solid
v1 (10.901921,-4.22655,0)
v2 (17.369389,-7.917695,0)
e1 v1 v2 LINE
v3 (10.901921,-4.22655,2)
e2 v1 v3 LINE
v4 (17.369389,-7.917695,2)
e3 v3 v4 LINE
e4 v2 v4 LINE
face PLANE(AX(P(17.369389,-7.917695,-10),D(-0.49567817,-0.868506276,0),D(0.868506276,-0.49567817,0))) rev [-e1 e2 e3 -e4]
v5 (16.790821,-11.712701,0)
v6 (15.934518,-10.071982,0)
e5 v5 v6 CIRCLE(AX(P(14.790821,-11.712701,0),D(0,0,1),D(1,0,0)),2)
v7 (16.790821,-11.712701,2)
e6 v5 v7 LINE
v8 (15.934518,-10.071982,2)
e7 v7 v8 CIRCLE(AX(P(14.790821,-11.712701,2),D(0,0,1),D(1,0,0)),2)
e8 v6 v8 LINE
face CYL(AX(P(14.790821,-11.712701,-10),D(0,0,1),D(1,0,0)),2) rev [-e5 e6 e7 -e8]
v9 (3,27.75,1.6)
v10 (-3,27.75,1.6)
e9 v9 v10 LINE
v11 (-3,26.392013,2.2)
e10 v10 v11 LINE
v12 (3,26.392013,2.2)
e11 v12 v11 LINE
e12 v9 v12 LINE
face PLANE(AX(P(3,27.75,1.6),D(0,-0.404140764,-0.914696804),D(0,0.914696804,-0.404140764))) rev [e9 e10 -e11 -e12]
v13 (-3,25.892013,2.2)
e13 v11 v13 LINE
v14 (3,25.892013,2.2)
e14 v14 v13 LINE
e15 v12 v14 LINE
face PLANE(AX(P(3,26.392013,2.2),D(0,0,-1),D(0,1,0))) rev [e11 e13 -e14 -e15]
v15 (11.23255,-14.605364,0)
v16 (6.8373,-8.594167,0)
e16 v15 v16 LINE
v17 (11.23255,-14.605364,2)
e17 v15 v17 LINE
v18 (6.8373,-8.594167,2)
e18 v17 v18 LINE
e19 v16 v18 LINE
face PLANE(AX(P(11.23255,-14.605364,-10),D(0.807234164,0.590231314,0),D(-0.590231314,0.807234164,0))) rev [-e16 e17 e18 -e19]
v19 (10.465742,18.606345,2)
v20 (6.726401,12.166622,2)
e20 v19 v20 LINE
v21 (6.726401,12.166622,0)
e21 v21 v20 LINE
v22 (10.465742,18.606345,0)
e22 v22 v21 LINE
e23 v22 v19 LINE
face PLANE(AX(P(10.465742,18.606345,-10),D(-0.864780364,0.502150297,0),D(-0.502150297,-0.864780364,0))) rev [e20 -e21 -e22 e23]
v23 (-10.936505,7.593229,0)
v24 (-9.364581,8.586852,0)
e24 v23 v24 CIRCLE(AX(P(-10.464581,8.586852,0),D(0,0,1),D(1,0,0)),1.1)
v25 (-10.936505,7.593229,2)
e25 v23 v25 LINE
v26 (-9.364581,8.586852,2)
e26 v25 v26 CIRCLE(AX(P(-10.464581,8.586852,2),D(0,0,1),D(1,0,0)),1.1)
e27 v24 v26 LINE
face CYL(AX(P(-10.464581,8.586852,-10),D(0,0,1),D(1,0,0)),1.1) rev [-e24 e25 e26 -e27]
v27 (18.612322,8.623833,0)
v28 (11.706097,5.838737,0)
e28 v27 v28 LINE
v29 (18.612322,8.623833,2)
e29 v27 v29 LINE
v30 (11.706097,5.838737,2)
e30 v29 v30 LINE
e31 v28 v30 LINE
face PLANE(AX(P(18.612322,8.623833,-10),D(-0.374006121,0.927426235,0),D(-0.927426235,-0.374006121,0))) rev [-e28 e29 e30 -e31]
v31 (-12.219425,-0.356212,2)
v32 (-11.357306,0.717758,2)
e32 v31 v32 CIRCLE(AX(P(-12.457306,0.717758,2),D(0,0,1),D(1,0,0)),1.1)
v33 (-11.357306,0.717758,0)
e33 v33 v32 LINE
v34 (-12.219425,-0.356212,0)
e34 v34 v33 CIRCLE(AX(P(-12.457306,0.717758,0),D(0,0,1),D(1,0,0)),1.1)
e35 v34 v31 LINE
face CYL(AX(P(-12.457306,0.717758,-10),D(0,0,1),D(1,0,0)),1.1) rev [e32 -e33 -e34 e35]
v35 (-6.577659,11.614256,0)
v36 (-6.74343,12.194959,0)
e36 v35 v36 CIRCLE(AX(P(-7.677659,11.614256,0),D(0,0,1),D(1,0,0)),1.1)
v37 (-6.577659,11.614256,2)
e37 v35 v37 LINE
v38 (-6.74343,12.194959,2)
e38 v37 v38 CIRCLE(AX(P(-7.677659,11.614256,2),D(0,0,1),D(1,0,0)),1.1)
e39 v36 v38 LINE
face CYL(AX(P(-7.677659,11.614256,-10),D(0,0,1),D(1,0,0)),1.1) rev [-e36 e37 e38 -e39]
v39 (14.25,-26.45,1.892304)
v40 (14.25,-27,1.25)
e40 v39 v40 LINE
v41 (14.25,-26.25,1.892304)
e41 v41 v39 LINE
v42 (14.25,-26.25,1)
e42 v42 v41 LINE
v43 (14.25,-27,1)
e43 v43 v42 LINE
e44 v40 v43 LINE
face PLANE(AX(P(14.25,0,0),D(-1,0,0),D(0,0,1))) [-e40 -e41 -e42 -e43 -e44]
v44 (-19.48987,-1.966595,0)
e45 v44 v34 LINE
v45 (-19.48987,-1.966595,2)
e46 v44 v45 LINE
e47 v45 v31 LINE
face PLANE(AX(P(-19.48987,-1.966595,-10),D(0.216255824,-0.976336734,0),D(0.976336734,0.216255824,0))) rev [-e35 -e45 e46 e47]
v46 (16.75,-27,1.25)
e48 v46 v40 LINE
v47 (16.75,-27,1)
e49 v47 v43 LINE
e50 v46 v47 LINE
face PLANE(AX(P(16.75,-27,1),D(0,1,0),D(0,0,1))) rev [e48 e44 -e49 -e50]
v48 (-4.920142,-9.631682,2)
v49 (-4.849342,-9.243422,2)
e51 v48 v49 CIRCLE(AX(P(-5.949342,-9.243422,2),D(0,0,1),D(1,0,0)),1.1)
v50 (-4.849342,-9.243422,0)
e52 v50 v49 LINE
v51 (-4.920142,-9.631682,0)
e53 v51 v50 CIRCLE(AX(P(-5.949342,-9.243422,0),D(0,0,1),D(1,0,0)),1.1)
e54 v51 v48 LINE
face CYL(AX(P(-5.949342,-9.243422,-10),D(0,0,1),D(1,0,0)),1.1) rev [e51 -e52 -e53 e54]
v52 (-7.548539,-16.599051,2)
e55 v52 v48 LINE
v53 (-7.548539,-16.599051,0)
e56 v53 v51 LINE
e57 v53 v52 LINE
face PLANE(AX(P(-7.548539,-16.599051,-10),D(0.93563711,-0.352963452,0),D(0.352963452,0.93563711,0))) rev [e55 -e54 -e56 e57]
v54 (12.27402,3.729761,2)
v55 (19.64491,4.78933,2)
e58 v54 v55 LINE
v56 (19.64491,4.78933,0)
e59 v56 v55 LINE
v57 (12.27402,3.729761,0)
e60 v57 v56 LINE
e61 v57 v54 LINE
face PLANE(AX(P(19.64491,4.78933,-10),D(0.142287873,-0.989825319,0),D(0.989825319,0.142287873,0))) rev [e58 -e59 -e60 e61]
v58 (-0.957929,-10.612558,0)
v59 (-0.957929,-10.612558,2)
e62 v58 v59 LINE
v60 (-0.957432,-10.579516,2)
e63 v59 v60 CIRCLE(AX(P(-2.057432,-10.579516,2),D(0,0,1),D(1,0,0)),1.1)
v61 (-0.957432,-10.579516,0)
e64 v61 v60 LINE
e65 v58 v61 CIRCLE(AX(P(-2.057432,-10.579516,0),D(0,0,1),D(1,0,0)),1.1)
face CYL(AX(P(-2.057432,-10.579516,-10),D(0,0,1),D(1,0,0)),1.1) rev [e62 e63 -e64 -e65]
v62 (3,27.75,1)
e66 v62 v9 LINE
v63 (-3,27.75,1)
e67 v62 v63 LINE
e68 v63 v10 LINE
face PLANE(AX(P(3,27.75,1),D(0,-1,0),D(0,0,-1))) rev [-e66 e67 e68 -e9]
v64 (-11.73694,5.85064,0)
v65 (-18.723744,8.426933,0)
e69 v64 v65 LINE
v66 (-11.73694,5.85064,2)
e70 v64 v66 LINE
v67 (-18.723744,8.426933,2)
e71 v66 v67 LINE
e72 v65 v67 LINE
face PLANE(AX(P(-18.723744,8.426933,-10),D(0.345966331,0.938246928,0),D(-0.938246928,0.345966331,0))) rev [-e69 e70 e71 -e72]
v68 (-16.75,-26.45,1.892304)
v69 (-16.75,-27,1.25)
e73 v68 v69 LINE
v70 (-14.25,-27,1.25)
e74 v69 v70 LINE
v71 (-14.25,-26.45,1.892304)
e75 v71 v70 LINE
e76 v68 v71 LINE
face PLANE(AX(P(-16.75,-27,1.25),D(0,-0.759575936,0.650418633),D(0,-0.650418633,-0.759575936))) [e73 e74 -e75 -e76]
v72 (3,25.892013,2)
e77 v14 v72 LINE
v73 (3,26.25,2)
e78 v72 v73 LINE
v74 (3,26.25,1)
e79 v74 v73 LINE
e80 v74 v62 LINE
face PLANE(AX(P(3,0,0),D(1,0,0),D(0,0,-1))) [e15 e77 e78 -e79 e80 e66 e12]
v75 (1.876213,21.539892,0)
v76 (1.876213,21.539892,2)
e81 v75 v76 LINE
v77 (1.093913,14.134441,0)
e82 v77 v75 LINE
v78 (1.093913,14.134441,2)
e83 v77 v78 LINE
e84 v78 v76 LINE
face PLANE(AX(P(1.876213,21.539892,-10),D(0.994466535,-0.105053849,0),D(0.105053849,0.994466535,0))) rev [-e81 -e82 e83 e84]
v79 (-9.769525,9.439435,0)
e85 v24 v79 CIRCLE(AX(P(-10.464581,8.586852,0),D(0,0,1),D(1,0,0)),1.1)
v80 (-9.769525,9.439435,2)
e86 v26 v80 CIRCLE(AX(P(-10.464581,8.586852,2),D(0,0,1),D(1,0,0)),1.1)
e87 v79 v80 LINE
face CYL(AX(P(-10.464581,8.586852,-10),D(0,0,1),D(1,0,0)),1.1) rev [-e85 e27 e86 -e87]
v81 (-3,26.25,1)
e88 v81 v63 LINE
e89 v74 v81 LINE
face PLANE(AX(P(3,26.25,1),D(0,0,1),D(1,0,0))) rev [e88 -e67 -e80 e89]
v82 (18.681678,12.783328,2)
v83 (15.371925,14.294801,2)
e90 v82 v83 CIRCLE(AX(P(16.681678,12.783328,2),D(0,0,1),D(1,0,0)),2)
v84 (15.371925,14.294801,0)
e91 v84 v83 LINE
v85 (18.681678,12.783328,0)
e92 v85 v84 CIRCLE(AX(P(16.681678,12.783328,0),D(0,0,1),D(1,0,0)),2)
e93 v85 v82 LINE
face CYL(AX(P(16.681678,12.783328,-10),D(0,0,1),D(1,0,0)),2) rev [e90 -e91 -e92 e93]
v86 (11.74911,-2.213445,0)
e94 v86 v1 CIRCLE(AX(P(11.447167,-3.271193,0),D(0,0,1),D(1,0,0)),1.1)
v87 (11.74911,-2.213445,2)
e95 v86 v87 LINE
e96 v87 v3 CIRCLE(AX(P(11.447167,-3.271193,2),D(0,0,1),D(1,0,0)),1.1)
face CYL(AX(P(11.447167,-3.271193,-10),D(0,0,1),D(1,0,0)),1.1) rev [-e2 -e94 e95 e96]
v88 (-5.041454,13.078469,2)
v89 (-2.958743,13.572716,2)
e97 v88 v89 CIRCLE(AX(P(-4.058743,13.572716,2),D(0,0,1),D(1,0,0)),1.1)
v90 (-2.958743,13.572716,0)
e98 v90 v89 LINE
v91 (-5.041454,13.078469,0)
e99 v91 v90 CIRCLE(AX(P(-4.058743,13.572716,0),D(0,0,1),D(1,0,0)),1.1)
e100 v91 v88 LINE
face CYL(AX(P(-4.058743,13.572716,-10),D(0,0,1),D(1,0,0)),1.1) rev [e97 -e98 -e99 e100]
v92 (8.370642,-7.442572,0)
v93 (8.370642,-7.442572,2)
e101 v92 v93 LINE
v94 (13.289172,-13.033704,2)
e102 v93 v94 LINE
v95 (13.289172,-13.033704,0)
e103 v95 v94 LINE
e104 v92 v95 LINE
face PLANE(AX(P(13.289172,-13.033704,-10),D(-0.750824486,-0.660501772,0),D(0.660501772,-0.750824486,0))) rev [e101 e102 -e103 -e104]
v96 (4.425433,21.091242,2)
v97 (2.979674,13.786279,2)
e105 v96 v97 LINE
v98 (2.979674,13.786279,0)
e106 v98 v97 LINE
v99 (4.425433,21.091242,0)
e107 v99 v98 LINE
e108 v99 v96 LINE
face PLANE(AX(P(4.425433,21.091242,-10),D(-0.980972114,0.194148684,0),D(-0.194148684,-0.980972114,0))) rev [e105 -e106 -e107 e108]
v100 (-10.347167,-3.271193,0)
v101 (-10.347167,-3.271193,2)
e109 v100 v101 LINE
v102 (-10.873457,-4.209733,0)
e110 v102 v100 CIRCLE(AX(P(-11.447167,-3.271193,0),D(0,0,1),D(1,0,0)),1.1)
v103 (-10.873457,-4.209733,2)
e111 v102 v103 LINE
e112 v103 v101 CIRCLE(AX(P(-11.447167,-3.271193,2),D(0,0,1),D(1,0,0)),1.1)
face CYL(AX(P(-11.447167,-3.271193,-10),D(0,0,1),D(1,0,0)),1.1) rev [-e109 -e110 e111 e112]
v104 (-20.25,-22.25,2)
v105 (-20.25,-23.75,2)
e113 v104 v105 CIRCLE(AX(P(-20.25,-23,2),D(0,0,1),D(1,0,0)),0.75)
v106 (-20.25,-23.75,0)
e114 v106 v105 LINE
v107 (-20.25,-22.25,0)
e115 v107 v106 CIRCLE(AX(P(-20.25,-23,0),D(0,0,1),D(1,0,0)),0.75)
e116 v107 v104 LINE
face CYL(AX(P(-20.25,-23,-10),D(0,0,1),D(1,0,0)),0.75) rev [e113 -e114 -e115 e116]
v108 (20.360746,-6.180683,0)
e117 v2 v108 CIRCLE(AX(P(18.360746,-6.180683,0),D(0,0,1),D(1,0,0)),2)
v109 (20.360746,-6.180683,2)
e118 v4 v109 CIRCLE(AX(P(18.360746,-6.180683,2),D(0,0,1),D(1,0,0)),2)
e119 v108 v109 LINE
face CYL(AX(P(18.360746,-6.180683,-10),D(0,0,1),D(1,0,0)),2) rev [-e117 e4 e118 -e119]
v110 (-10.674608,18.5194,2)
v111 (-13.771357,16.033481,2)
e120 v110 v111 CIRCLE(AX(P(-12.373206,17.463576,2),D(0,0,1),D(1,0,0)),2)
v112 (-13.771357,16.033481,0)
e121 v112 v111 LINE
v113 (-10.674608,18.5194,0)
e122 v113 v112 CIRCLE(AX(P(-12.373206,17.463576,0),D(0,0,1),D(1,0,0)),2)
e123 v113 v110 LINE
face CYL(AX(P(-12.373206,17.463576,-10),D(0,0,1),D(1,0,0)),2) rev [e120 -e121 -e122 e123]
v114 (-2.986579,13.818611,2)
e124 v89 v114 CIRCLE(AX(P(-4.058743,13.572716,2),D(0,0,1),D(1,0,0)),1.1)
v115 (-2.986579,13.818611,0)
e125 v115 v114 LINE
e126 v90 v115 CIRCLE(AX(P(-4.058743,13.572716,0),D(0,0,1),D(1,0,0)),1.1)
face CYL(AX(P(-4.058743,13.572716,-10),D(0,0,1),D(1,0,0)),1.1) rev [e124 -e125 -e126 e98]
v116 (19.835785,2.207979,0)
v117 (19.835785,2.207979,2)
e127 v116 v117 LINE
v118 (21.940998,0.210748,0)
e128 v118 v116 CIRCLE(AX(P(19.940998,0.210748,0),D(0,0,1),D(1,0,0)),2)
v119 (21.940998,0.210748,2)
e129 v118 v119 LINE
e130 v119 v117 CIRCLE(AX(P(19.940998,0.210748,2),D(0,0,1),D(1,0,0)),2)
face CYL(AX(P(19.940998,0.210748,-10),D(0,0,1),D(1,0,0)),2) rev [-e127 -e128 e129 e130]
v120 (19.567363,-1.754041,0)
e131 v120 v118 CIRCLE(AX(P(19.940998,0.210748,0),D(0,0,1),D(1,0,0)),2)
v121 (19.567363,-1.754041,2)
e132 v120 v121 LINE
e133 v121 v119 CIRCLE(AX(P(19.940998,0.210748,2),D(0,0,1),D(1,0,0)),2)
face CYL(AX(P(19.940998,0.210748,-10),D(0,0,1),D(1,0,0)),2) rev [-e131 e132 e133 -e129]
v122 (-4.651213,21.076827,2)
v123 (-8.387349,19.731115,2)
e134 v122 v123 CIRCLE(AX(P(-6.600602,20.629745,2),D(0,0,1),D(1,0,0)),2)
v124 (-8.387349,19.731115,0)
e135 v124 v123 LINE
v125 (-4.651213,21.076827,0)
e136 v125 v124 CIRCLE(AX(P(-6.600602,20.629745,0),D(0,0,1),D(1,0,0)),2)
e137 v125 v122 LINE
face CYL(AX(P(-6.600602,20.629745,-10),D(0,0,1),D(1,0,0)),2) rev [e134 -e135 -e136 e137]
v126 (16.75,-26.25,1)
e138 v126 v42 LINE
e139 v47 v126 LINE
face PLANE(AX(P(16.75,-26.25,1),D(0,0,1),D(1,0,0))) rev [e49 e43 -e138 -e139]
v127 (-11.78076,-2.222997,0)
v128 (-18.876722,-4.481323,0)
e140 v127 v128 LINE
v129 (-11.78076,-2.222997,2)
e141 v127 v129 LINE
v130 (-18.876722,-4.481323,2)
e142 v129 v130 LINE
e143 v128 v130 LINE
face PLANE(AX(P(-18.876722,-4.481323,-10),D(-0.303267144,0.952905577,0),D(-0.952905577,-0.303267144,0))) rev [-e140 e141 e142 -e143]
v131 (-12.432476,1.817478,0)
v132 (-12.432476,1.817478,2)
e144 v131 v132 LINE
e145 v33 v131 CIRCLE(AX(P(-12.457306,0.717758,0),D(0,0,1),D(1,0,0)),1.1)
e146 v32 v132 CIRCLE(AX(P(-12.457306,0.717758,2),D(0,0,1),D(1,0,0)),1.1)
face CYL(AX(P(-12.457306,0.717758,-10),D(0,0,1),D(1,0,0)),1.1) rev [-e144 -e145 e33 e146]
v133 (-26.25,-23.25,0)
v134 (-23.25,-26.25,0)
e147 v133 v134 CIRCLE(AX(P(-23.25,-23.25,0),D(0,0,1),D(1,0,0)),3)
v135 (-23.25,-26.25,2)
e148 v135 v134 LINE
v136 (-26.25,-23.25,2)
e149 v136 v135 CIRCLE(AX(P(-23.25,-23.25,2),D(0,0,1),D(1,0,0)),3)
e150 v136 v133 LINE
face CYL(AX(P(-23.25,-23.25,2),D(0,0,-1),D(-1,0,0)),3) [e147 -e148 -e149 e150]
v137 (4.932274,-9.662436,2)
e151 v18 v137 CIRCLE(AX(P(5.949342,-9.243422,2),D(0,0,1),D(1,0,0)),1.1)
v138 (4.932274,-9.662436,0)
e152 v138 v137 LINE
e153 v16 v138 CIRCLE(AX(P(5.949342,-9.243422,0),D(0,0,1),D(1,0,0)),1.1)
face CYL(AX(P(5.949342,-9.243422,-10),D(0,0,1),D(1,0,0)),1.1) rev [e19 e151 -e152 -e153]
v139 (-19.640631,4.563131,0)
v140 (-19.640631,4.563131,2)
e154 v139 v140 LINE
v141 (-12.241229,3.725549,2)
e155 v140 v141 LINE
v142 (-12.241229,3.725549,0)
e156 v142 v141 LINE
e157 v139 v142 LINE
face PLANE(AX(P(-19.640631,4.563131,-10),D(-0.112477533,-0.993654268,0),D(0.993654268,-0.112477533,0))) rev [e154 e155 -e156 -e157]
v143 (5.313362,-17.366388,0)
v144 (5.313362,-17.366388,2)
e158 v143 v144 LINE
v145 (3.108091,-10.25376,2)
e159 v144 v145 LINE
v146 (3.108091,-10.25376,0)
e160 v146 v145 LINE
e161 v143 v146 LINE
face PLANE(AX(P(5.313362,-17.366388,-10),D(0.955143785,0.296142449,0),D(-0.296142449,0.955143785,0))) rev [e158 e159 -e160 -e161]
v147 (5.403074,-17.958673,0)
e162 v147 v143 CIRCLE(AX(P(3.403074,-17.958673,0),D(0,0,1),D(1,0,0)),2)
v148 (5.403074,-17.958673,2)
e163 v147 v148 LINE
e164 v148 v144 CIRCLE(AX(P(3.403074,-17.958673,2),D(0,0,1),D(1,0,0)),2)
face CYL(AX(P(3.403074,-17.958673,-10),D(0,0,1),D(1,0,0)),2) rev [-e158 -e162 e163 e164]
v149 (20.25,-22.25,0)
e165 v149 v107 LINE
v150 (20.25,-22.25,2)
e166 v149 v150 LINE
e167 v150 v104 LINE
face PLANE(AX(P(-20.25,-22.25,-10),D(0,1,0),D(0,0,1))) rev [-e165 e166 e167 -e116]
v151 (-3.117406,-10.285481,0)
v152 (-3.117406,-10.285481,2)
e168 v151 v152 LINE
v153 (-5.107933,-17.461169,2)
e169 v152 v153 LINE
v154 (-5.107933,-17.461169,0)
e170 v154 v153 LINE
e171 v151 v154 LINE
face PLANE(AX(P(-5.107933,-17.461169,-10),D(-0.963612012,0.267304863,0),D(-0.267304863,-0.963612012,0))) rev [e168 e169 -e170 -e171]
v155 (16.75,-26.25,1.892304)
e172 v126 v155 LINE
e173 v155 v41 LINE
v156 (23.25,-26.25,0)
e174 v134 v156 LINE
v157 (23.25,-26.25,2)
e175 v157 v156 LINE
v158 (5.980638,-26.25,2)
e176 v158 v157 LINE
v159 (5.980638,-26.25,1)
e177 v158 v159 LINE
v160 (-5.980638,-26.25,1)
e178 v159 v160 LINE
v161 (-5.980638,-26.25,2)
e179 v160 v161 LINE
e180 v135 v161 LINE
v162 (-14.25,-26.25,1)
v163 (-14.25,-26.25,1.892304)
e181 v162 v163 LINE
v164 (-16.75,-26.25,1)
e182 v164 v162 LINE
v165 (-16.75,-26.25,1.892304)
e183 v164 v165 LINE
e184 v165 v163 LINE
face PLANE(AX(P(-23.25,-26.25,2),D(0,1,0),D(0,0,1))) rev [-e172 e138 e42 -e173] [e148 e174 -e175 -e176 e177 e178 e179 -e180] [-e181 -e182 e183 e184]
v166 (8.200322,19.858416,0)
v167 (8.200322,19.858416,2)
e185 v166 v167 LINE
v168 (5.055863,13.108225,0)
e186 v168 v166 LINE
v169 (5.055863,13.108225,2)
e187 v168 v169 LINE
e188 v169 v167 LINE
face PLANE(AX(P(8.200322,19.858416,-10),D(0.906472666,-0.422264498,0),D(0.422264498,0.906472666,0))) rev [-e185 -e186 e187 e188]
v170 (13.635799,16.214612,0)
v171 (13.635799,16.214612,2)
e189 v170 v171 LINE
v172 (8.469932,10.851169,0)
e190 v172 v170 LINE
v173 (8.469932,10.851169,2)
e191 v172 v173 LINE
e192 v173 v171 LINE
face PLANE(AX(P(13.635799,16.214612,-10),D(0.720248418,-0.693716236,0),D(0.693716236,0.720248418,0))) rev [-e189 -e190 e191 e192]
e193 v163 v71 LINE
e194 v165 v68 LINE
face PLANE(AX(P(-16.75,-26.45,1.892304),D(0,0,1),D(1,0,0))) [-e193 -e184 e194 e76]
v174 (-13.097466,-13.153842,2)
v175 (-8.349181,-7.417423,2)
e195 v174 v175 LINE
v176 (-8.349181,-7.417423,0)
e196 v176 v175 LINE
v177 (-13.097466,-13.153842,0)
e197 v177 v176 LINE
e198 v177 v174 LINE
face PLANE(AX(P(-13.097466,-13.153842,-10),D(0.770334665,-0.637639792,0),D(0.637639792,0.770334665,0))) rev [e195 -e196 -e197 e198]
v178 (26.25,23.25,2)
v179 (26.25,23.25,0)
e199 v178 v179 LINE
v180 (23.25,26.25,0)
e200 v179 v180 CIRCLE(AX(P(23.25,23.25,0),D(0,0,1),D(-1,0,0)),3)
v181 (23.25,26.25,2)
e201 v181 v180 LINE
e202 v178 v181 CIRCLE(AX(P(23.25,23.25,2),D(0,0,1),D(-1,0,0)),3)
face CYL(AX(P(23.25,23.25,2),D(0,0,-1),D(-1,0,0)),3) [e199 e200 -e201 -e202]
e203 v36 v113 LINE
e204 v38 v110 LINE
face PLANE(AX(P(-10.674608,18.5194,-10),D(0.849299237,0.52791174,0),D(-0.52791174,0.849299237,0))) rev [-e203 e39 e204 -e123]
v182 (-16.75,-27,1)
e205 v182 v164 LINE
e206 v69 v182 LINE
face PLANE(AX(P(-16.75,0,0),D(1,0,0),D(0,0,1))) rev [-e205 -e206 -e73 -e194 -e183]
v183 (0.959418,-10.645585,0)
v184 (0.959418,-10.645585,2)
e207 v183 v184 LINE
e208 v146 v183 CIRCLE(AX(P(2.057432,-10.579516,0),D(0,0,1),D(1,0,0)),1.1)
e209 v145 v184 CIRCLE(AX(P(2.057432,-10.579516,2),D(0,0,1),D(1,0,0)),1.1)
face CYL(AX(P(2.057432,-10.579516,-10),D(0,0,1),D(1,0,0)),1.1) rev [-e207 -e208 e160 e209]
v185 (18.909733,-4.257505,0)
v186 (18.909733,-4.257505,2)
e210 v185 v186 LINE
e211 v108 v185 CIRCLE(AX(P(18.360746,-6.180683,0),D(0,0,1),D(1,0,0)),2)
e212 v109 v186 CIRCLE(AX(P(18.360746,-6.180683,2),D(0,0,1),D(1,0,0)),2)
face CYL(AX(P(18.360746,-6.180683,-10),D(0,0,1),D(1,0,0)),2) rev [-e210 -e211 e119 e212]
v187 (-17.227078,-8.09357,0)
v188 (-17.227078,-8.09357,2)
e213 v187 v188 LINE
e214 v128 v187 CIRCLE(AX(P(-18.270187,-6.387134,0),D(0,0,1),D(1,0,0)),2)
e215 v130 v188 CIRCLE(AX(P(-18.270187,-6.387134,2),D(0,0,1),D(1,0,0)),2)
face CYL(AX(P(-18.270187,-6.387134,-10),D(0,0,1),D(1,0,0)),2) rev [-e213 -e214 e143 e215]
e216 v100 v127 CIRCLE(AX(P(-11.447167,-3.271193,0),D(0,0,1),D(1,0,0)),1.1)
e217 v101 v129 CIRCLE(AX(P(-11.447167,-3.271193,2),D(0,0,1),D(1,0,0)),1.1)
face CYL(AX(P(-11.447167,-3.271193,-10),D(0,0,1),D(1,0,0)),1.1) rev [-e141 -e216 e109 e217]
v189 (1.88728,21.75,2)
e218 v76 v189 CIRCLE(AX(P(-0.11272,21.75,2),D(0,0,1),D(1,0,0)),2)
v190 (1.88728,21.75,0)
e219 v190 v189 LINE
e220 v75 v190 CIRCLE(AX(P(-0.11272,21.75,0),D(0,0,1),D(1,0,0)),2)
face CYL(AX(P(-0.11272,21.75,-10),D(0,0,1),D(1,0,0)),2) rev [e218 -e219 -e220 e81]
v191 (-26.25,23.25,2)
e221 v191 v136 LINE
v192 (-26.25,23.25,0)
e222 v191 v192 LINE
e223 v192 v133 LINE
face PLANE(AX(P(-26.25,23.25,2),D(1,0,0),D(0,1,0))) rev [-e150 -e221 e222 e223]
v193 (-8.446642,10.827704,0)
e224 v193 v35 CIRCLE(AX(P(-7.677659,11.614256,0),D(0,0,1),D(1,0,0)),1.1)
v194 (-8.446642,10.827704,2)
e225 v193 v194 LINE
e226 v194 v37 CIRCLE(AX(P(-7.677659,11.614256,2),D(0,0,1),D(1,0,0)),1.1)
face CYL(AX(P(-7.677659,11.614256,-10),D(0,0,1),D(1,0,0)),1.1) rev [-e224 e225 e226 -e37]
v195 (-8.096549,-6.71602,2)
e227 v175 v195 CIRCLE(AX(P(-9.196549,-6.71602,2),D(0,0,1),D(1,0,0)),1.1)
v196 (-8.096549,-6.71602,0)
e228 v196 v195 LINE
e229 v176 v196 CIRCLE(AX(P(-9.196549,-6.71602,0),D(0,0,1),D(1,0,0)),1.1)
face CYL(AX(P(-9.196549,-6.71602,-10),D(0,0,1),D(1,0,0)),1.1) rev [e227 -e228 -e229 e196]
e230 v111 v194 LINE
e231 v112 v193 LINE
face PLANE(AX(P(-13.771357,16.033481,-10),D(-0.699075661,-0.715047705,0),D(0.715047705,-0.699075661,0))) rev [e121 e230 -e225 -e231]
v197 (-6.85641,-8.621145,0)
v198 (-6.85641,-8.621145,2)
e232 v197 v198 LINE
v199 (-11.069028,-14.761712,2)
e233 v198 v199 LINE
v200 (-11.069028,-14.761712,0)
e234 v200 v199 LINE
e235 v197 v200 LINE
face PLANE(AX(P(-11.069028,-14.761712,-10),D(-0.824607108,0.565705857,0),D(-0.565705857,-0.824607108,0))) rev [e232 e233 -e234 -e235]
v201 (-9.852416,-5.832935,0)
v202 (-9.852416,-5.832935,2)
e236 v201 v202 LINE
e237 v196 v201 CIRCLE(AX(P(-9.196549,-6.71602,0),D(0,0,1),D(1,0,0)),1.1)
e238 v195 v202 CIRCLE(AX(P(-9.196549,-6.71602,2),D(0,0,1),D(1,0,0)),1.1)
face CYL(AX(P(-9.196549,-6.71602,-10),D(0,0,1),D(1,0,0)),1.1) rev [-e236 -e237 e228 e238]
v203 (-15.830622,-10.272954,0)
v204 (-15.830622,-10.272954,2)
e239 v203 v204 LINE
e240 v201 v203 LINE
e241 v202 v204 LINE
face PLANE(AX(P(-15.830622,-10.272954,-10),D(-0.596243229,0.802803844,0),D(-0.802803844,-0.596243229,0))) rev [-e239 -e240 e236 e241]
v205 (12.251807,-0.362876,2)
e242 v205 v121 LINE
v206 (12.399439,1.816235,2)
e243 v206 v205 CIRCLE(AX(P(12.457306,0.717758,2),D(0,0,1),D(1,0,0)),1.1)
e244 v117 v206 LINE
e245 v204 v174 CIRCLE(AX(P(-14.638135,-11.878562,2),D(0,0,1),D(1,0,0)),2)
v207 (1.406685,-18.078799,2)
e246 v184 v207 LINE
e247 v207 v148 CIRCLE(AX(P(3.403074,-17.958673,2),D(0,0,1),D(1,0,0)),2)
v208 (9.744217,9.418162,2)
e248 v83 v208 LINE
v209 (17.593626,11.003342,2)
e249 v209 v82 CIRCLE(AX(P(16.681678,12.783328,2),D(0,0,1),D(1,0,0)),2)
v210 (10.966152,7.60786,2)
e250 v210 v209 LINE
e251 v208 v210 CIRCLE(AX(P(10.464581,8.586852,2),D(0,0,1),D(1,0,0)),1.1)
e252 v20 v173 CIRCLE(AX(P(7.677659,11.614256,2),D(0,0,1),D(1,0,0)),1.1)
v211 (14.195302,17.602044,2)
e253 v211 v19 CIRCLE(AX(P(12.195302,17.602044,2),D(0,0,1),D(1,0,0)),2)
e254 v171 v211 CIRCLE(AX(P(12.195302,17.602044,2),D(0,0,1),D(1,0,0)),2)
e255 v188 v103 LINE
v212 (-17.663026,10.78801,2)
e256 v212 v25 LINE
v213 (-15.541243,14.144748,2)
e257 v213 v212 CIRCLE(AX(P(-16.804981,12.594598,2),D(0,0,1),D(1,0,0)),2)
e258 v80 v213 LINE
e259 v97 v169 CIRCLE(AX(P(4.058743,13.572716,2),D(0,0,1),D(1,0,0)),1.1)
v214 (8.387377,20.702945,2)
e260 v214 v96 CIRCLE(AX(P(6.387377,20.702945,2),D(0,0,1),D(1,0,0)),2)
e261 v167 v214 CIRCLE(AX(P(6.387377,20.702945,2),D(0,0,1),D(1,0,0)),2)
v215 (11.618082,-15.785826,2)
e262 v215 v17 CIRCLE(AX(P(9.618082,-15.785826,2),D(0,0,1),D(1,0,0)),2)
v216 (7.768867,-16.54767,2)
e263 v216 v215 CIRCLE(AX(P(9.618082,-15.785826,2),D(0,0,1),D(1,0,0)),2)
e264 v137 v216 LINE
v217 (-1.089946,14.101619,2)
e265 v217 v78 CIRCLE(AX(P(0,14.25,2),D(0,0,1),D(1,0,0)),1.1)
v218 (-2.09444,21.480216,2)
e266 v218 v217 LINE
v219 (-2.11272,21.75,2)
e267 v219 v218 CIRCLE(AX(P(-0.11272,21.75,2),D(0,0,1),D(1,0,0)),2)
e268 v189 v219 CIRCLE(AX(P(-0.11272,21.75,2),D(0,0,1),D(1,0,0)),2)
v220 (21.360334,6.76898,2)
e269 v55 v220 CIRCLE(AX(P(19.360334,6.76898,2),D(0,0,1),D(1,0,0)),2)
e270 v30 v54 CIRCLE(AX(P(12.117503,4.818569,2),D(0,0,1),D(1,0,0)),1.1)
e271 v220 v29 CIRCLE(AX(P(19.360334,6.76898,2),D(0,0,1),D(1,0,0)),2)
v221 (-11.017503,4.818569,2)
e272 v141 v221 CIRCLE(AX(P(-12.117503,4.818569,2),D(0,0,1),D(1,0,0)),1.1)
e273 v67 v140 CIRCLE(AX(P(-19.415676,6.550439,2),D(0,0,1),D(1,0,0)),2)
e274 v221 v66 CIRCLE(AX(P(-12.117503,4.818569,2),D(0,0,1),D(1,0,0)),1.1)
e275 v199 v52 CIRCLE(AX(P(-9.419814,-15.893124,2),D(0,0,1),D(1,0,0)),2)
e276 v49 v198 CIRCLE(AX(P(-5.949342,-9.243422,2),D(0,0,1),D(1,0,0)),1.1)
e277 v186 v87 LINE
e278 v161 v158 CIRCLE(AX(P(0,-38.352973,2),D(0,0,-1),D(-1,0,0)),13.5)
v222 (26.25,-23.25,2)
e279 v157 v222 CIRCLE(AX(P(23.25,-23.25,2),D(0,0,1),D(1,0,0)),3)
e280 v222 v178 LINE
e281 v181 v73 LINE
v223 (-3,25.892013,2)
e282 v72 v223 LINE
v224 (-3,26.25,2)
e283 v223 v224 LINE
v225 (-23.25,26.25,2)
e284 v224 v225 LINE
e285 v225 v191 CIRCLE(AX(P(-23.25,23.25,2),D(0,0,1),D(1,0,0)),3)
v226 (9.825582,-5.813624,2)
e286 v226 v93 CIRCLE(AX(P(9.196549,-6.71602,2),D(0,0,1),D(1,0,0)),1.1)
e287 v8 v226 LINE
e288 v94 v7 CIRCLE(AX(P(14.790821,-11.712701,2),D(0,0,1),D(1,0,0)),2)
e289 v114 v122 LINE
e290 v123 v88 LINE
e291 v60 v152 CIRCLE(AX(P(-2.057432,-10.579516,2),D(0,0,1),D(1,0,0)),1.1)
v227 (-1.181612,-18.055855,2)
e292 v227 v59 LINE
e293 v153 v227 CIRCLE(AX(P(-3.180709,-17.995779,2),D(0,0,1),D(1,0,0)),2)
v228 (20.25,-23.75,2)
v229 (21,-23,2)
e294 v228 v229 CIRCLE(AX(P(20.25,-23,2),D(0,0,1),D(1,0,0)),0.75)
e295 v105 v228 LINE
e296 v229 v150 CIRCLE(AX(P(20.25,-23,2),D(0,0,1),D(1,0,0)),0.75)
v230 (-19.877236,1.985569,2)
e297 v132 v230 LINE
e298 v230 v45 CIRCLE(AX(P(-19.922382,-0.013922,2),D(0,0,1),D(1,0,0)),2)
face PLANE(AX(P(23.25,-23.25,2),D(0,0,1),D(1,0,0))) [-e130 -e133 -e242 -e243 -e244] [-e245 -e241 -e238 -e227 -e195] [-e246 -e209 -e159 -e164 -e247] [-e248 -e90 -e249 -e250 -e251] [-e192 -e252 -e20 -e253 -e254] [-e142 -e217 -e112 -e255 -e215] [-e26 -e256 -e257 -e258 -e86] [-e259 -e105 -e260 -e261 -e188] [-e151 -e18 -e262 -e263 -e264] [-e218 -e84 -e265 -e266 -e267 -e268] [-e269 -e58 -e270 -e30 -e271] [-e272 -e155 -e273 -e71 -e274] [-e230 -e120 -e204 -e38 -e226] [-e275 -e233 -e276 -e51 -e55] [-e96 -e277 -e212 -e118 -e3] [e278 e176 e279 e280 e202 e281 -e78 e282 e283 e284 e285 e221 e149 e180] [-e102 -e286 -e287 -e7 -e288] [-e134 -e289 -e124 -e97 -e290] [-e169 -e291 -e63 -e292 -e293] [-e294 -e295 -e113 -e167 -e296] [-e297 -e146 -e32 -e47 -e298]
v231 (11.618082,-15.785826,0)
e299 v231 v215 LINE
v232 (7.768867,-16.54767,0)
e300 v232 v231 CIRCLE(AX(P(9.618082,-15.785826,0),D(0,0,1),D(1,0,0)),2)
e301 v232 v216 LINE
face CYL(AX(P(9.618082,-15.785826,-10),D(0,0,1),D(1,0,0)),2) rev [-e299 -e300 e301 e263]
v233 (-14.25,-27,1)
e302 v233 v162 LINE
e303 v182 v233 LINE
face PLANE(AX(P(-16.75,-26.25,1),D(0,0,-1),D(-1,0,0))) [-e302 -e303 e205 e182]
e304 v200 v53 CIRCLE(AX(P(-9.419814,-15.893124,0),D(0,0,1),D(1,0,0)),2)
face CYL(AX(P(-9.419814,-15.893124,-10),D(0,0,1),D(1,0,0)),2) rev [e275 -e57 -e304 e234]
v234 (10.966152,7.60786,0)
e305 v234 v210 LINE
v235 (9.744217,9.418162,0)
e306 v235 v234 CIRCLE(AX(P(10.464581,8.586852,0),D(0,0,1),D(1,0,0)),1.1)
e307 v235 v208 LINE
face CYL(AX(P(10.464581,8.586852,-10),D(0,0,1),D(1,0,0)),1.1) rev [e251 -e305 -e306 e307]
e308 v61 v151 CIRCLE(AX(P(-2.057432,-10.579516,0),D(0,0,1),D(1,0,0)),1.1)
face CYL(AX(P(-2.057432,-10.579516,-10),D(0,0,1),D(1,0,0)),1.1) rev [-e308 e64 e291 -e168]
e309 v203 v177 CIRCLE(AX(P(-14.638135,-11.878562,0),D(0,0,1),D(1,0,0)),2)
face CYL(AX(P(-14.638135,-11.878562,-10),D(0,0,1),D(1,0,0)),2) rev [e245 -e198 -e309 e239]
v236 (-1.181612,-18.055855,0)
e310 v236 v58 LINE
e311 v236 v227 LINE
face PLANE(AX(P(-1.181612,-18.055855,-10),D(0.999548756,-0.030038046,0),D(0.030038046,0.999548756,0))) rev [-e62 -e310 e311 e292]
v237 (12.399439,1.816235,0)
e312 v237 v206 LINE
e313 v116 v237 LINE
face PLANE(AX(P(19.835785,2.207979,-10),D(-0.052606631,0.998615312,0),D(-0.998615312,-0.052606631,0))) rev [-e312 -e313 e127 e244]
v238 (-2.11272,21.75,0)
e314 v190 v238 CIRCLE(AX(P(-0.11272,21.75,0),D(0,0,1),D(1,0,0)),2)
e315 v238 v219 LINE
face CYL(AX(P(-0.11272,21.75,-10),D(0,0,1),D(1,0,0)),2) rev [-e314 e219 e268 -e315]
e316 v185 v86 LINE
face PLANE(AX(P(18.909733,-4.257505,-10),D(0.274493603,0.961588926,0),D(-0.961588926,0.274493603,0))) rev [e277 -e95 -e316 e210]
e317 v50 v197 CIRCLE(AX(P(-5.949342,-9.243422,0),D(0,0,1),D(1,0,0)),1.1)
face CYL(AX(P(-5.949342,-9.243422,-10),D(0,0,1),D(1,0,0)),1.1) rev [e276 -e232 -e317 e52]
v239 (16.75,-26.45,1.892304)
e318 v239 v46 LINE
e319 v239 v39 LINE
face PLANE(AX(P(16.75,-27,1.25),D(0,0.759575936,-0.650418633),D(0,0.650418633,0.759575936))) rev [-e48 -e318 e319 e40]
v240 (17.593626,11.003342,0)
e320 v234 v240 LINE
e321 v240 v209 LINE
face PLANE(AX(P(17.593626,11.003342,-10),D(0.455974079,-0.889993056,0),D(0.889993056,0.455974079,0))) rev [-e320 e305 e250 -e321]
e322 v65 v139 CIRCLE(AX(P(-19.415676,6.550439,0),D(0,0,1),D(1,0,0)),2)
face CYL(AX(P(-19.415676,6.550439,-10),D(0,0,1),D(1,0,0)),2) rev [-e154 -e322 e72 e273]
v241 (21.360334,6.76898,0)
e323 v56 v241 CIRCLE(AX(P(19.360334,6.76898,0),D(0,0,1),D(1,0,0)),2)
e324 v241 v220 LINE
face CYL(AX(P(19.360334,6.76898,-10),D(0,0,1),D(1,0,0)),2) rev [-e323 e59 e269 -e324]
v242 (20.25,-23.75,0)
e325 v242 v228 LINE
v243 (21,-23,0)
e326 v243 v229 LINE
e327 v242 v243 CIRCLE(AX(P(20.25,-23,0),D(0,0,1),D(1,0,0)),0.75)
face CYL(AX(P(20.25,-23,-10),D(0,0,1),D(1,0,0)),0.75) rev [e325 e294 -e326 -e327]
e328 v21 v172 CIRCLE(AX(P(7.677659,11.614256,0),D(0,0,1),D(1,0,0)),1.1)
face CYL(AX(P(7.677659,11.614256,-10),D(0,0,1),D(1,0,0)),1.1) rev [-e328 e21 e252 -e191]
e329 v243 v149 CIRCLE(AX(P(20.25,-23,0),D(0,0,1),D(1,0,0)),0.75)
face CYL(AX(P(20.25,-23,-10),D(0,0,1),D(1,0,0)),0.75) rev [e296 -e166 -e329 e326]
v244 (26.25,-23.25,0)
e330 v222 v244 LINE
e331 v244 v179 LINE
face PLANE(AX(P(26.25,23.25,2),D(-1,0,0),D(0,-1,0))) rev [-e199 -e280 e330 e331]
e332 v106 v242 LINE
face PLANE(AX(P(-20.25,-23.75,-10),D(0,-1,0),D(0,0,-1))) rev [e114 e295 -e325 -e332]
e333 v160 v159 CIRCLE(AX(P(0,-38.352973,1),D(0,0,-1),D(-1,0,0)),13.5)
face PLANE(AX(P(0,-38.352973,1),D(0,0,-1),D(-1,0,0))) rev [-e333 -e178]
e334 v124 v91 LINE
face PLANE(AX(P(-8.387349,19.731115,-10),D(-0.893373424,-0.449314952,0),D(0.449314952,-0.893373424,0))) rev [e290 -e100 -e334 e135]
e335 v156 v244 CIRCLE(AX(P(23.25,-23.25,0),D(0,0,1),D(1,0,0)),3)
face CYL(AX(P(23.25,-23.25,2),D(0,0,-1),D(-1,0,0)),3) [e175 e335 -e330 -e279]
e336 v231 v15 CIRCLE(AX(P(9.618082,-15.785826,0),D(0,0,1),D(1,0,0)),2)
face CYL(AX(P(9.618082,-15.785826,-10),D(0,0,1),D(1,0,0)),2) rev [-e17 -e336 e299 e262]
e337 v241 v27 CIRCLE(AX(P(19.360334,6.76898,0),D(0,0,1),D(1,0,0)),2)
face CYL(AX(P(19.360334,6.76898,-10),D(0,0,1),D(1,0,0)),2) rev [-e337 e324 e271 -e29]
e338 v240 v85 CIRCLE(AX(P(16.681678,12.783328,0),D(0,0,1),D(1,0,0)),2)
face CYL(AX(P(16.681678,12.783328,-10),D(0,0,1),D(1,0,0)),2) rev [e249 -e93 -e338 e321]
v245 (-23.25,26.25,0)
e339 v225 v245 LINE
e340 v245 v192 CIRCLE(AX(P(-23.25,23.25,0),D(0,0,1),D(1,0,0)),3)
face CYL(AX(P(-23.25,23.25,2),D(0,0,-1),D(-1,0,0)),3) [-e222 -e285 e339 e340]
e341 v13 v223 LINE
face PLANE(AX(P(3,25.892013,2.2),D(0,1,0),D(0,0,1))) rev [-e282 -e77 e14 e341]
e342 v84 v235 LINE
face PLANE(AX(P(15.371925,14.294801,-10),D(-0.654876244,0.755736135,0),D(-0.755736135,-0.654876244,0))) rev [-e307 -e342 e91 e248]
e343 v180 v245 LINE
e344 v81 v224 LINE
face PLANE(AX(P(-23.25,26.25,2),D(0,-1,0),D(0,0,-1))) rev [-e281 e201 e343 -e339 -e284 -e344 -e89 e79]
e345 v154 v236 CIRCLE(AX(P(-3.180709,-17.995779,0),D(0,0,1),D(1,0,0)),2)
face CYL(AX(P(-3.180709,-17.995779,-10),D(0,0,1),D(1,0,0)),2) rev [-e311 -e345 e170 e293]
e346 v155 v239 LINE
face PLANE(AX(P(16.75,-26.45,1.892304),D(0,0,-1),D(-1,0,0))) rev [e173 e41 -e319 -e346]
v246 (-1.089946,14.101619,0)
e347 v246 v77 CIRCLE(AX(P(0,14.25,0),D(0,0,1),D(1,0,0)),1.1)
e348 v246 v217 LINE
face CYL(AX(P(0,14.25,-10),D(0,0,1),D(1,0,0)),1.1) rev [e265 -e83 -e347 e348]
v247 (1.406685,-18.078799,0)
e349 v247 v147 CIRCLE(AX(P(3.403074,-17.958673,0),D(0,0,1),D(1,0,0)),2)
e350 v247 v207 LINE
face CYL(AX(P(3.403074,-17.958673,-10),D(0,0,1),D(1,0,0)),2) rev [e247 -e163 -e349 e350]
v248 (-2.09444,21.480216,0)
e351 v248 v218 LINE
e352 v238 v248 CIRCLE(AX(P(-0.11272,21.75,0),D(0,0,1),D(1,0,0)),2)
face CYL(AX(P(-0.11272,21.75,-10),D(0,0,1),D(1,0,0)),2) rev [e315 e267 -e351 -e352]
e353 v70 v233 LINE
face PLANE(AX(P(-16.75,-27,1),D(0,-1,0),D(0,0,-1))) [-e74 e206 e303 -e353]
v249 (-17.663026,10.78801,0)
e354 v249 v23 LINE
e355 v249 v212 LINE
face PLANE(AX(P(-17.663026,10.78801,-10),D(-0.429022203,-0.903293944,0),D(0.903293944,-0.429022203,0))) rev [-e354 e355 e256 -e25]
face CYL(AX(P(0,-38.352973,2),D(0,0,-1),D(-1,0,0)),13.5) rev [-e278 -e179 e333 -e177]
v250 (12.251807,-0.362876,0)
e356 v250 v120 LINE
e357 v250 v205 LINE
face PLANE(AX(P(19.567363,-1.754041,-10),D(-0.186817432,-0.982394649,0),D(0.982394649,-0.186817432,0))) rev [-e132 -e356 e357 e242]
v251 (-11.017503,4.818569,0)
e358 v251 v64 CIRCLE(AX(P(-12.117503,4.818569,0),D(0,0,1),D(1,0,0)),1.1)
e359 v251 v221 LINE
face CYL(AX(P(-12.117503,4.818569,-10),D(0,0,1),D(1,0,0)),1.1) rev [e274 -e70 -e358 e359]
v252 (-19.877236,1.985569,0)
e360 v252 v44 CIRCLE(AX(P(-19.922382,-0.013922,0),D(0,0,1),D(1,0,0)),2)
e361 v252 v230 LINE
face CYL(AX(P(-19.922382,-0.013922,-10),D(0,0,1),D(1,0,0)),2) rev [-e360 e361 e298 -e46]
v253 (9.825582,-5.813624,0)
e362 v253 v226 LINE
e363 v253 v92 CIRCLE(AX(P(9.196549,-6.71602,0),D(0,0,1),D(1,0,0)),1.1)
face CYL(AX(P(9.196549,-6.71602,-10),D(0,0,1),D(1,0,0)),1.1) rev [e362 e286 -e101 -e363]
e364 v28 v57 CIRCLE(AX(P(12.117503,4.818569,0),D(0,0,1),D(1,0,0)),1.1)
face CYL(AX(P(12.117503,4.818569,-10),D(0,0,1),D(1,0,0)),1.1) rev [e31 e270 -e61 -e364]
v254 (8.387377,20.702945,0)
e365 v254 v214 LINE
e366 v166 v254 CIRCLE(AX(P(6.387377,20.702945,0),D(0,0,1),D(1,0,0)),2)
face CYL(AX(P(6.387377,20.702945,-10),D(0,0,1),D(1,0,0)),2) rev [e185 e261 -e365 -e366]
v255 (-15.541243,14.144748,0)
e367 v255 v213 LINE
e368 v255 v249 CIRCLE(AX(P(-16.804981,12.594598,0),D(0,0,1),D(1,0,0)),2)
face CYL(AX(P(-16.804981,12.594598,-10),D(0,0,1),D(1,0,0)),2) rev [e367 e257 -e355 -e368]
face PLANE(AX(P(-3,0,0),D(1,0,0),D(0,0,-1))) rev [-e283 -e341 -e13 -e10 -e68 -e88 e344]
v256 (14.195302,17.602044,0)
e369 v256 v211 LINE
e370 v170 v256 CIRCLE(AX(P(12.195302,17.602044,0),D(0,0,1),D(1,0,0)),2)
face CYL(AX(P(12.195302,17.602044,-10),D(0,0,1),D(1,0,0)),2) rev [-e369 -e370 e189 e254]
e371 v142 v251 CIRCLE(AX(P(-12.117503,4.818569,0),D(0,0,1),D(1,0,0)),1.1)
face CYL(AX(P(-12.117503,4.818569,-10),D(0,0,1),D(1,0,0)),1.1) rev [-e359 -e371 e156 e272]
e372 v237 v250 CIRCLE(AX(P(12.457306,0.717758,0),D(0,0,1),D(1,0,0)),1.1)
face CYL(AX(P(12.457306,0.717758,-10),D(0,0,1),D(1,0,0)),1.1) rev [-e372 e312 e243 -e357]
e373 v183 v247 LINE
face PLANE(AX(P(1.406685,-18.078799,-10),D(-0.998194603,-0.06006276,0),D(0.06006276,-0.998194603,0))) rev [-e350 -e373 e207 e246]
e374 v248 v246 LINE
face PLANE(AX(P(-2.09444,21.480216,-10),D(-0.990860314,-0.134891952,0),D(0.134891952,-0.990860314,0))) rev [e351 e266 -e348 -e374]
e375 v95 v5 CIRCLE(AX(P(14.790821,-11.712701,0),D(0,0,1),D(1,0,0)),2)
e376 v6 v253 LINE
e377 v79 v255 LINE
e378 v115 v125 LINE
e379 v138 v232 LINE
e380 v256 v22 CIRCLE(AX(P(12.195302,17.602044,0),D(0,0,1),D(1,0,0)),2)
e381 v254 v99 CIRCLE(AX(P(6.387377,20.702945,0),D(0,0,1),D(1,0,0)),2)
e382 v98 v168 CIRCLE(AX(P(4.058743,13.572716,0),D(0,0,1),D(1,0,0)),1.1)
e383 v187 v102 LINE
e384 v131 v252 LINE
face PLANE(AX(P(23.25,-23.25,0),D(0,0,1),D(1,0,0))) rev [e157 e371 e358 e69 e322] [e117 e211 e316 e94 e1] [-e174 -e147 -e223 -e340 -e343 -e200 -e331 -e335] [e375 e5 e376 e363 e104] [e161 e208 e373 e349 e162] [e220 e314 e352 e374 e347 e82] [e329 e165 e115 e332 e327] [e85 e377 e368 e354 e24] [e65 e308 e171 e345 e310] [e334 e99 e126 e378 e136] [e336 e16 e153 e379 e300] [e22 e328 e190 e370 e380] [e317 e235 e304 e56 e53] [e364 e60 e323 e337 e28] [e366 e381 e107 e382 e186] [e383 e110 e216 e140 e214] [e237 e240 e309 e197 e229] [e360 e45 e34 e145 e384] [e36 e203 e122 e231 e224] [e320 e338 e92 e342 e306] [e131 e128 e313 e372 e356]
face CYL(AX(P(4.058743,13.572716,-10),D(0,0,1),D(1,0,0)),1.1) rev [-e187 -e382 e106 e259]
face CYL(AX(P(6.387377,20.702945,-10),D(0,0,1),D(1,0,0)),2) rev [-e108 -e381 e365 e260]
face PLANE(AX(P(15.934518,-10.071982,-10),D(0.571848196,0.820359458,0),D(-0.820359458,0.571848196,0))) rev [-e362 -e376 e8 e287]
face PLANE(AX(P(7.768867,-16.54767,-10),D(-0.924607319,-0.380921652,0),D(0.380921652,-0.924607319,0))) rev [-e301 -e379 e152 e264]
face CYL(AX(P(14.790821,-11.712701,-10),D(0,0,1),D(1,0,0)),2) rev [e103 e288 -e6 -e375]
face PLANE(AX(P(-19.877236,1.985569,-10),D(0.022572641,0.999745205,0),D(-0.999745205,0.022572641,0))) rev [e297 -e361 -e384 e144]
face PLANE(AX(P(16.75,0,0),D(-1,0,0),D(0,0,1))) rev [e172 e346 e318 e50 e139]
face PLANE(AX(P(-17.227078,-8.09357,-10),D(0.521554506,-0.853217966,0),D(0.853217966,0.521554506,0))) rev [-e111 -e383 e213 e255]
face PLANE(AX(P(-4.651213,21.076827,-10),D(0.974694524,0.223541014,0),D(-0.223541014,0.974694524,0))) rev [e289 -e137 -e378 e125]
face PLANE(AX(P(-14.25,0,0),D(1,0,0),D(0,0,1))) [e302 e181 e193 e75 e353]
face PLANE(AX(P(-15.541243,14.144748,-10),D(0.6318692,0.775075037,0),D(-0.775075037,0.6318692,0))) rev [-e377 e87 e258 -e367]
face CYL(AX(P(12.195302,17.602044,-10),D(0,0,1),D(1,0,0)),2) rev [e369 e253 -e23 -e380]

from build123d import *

# Parameters (mm, degrees)
BOSS_EXTRUDE1_DEPTH = 2
CUT_EXTRUDE1_DEPTH  = 12
CUT_EXTRUDE2_START  = -1
SKETCH3_R           = 13.5
CUT_EXTRUDE2_DEPTH  = 1
BOSS_EXTRUDE2_START = 14.25
BOSS_EXTRUDE2_DEPTH = 2.5
BOSS_EXTRUDE3_DEPTH = 3


with BuildPart() as part:
    # Sketch1 → Boss-Extrude1 (new body)
    with BuildSketch(Plane.XY):
        with BuildLine():
            Line((-23.25, 26.25), (23.25, 26.25))
            ThreePointArc((23.25, 26.25), (25.371320344, 25.371320344), (26.25, 23.25))
            Line((26.25, 23.25), (26.25, -23.25))
            ThreePointArc((26.25, -23.25), (25.371320344, -25.371320344), (23.25, -26.25))
            Line((23.25, -26.25), (-23.25, -26.25))
            ThreePointArc((-23.25, -26.25), (-25.371320344, -25.371320344), (-26.25, -23.25))
            Line((-26.25, -23.25), (-26.25, 23.25))
            ThreePointArc((-26.25, 23.25), (-25.371320344, 25.371320344), (-23.25, 26.25))
        make_face()
    extrude(amount=BOSS_EXTRUDE1_DEPTH)

    # Sketch2 → Cut-Extrude1 (cut)
    with BuildSketch(Plane.XY.offset(2)):
        with BuildLine():
            Line((-20.25, -22.25), (20.25, -22.25))
            ThreePointArc((20.25, -22.25), (21, -23), (20.25, -23.75))
            Line((20.25, -23.75), (-20.25, -23.75))
            ThreePointArc((-20.25, -23.75), (-21, -23), (-20.25, -22.25))
        make_face()
        with BuildLine():
            Line((-2.094440492, 21.480216096), (-1.089946345, 14.101618853))
            ThreePointArc((-1.089946345, 14.101618853), (0.01653038, 13.150124213), (1.093913188, 14.134440766))
            Line((1.093913188, 14.134440766), (1.876213205, 21.539892302))
            ThreePointArc((1.876213205, 21.539892302), (-0.1427751, 23.749774158), (-2.094440492, 21.480216096))
        make_face()
        with BuildLine():
            Line((4.425432765, 21.091242282), (2.97967404, 13.786279074))
            ThreePointArc((2.97967404, 13.786279074), (3.717248999, 12.527066633), (5.055863298, 13.108224574))
            Line((5.055863298, 13.108224574), (8.200322325, 19.858415919))
            ThreePointArc((8.200322325, 19.858415919), (7.00827584, 22.604124711), (4.425432765, 21.091242282))
        make_face()
        with BuildLine():
            Line((10.465741714, 18.606344756), (6.726400508, 12.166621695))
            ThreePointArc((6.726400508, 12.166621695), (7.01514601, 10.736146659), (8.469932169, 10.851168508))
            Line((8.469932169, 10.851168508), (13.635799279, 16.21461169))
            ThreePointArc((13.635799279, 16.21461169), (13.399871349, 19.198607267), (10.465741714, 18.606344756))
        make_face()
        with BuildLine():
            Line((15.371925155, 14.294800723), (9.74421711, 9.418161725))
            ThreePointArc((9.74421711, 9.418161725), (9.5528431, 7.971438261), (10.966152465, 7.607859615))
            Line((10.966152465, 7.607859615), (17.593625801, 11.003342342))
            ThreePointArc((17.593625801, 11.003342342), (18.339382876, 13.902262483), (15.371925155, 14.294800723))
        make_face()
        with BuildLine():
            Line((18.612321986, 8.623832879), (11.706096591, 5.838737448))
            ThreePointArc((11.706096591, 5.838737448), (11.055341412, 4.532540491), (12.274019984, 3.729760739))
            Line((12.274019984, 3.729760739), (19.644909973, 4.789329772))
            ThreePointArc((19.644909973, 4.789329772), (21.291537704, 7.289031496), (18.612321986, 8.623832879))
        make_face()
        with BuildLine():
            Line((19.83578493, 2.207978584), (12.399438868, 1.816235025))
            ThreePointArc((12.399438868, 1.816235025), (11.359821941, 0.792111284), (12.251806987, -0.362875933))
            Line((12.251806987, -0.362875933), (19.567363328, -1.754041339))
            ThreePointArc((19.567363328, -1.754041339), (21.93642405, 0.0755605), (19.83578493, 2.207978584))
        make_face()
        with BuildLine():
            Line((18.909732793, -4.257504797), (11.749109546, -2.21344499))
            ThreePointArc((11.749109546, -2.21344499), (10.433289497, -2.844515818), (10.901920596, -4.226549712))
            Line((10.901920596, -4.226549712), (17.369389247, -7.917695201))
            ThreePointArc((17.369389247, -7.917695201), (20.204158471, -6.956458994), (18.909732793, -4.257504797))
        make_face()
        with BuildLine():
            Line((15.934517692, -10.071981817), (9.825581899, -5.813624241))
            ThreePointArc((9.825581899, -5.813624241), (8.376148247, -5.98325584), (8.370641949, -7.442571595))
            Line((8.370641949, -7.442571595), (13.289172328, -13.033704277))
            ThreePointArc((13.289172328, -13.033704277), (16.282458822, -13.044998562), (15.934517692, -10.071981817))
        make_face()
        with BuildLine():
            Line((11.232550351, -14.60536367), (6.837299994, -8.594167444))
            ThreePointArc((6.837299994, -8.594167444), (5.411321364, -8.283977597), (4.932274362, -9.662435707))
            Line((4.932274362, -9.662435707), (7.768867384, -16.547669603))
            ThreePointArc((7.768867384, -16.547669603), (10.596302111, -17.530270468), (11.232550351, -14.60536367))
        make_face()
        with BuildLine():
            Line((5.313361888, -17.36638809), (3.108090542, -10.253759599))
            ThreePointArc((3.108090542, -10.253759599), (1.860093847, -9.497362189), (0.959418316, -10.645585329))
            Line((0.959418316, -10.645585329), (1.406685112, -18.078798509))
            ThreePointArc((1.406685112, -18.078798509), (3.761871648, -19.926225904), (5.313361888, -17.36638809))
        make_face()
        with BuildLine():
            Line((-1.181611781, -18.055855239), (-0.957928747, -10.612558143))
            ThreePointArc((-0.957928747, -10.612558143), (-1.892703701, -9.491920567), (-3.117405592, -10.285480943))
            Line((-3.117405592, -10.285480943), (-5.107933318, -17.461169421))
            ThreePointArc((-5.107933318, -17.461169421), (-3.48021598, -19.973225922), (-1.181611781, -18.055855239))
        make_face()
        with BuildLine():
            Line((-7.548539479, -16.599050654), (-4.920141592, -9.631681687))
            ThreePointArc((-4.920141592, -9.631681687), (-5.440397435, -8.268242415), (-6.856410232, -8.621145447))
            Line((-6.856410232, -8.621145447), (-11.069027916, -14.761712035))
            ThreePointArc((-11.069027916, -14.761712035), (-10.345168205, -17.666177341), (-7.548539479, -16.599050654))
        make_face()
        with BuildLine():
            Line((-13.097465797, -13.153841715), (-8.349180752, -7.417423416))
            ThreePointArc((-8.349180752, -7.417423416), (-8.39853969, -5.958932248), (-9.852416435, -5.832935417))
            Line((-9.852416435, -5.832935417), (-15.830621585, -10.272954444))
            ThreePointArc((-15.830621585, -10.272954444), (-16.089060933, -13.255084672), (-13.097465797, -13.153841715))
        make_face()
        with BuildLine():
            Line((-17.227078467, -8.09357027), (-10.873456626, -4.209732571))
            ThreePointArc((-10.873456626, -4.209732571), (-10.446569853, -2.814239656), (-11.780760442, -2.222996673))
            Line((-11.780760442, -2.222996673), (-18.876721768, -4.481323183))
            ThreePointArc((-18.876721768, -4.481323183), (-20.089454262, -7.217958251), (-17.227078467, -8.09357027))
        make_face()
        with BuildLine():
            Line((-19.48986988, -1.966595247), (-12.219424756, -0.356212226))
            ThreePointArc((-12.219424756, -0.356212226), (-11.362552077, 0.825059124), (-12.432476257, 1.817477908))
            Line((-12.432476257, 1.817477908), (-19.877236245, 1.985568633))
            ThreePointArc((-19.877236245, 1.985568633), (-21.912843501, -0.209014401), (-19.48986988, -1.966595247))
        make_face()
        with BuildLine():
            Line((-19.640631475, 4.56313054), (-12.24122861, 3.725548894))
            ThreePointArc((-12.24122861, 3.725548894), (-11.047225476, 4.564589601), (-11.73694036, 5.85064021))
            Line((-11.73694036, 5.85064021), (-18.723743748, 8.426932933))
            ThreePointArc((-18.723743748, 8.426932933), (-21.361636134, 7.012219056), (-19.640631475, 4.56313054))
        make_face()
        with BuildLine():
            Line((-17.663025894, 10.788009983), (-10.936505402, 7.593228638))
            ThreePointArc((-10.936505402, 7.593228638), (-9.534760578, 7.999115621), (-9.769524858, 9.439434518))
            Line((-9.769524858, 9.439434518), (-15.541243087, 14.144747946))
            ThreePointArc((-15.541243087, 14.144747946), (-18.495564033, 13.663209427), (-17.663025894, 10.788009983))
        make_face()
        with BuildLine():
            Line((-13.771357387, 16.033480805), (-8.446642136, 10.827703892))
            ThreePointArc((-8.446642136, 10.827703892), (-6.989056426, 10.756452998), (-6.743429747, 12.194959282))
            Line((-6.743429747, 12.194959282), (-10.67460759, 18.519399695))
            ThreePointArc((-10.67460759, 18.519399695), (-13.625210579, 19.023218704), (-13.771357387, 16.033480805))
        make_face()
        with BuildLine():
            Line((-8.387348622, 19.73111485), (-5.041454131, 13.078469074))
            ThreePointArc((-5.041454131, 13.078469074), (-3.685979563, 12.537801444), (-2.986579389, 13.818610637))
            Line((-2.986579389, 13.818610637), (-4.651212727, 21.076826783))
            ThreePointArc((-4.651212727, 21.076826783), (-7.278354143, 22.511406713), (-8.387348622, 19.73111485))
        make_face()
    extrude(amount=-CUT_EXTRUDE1_DEPTH, mode=Mode.SUBTRACT)

    # Sketch3 → Cut-Extrude2 (cut)
    with BuildSketch(Plane(origin=(0, 0, 0), x_dir=(-1, 0, 0), z_dir=(0, 0, -1)).offset(CUT_EXTRUDE2_START)):
        with Locations((0, -38.352973417)):
            Circle(SKETCH3_R)
    extrude(amount=-CUT_EXTRUDE2_DEPTH, mode=Mode.SUBTRACT)

    # Sketch4 → Boss-Extrude2 (add)
    with BuildSketch(Plane(origin=(0, 0, 0), x_dir=(0, 0, -1), z_dir=(1, 0, 0)).offset(BOSS_EXTRUDE2_START)):
        Polygon((-1, -26.25), (-1, -27), (-1.25, -27), (-1.892304423, -26.45), (-1.892304423, -26.25), align=None)
    boss_extrude2 = extrude(amount=BOSS_EXTRUDE2_DEPTH)

    # Mirror3: Boss-Extrude2 across plane
    add(boss_extrude2.mirror(Plane(origin=(0, 0, 0), x_dir=(0, 0, 1), z_dir=(1, 0, 0))))

    # Sketch5 → Boss-Extrude3 (add, symmetric)
    with BuildSketch(Plane(origin=(0, 0, 0), x_dir=(0, 0, -1), z_dir=(1, 0, 0))):
        Polygon((-1, 26.25), (-1, 27.75), (-1.6, 27.75), (-2.2, 26.392012559), (-2.2, 25.892012559), (-1, 25.892012559), align=None)
    extrude(amount=BOSS_EXTRUDE3_DEPTH, both=True)


solid = part.part
